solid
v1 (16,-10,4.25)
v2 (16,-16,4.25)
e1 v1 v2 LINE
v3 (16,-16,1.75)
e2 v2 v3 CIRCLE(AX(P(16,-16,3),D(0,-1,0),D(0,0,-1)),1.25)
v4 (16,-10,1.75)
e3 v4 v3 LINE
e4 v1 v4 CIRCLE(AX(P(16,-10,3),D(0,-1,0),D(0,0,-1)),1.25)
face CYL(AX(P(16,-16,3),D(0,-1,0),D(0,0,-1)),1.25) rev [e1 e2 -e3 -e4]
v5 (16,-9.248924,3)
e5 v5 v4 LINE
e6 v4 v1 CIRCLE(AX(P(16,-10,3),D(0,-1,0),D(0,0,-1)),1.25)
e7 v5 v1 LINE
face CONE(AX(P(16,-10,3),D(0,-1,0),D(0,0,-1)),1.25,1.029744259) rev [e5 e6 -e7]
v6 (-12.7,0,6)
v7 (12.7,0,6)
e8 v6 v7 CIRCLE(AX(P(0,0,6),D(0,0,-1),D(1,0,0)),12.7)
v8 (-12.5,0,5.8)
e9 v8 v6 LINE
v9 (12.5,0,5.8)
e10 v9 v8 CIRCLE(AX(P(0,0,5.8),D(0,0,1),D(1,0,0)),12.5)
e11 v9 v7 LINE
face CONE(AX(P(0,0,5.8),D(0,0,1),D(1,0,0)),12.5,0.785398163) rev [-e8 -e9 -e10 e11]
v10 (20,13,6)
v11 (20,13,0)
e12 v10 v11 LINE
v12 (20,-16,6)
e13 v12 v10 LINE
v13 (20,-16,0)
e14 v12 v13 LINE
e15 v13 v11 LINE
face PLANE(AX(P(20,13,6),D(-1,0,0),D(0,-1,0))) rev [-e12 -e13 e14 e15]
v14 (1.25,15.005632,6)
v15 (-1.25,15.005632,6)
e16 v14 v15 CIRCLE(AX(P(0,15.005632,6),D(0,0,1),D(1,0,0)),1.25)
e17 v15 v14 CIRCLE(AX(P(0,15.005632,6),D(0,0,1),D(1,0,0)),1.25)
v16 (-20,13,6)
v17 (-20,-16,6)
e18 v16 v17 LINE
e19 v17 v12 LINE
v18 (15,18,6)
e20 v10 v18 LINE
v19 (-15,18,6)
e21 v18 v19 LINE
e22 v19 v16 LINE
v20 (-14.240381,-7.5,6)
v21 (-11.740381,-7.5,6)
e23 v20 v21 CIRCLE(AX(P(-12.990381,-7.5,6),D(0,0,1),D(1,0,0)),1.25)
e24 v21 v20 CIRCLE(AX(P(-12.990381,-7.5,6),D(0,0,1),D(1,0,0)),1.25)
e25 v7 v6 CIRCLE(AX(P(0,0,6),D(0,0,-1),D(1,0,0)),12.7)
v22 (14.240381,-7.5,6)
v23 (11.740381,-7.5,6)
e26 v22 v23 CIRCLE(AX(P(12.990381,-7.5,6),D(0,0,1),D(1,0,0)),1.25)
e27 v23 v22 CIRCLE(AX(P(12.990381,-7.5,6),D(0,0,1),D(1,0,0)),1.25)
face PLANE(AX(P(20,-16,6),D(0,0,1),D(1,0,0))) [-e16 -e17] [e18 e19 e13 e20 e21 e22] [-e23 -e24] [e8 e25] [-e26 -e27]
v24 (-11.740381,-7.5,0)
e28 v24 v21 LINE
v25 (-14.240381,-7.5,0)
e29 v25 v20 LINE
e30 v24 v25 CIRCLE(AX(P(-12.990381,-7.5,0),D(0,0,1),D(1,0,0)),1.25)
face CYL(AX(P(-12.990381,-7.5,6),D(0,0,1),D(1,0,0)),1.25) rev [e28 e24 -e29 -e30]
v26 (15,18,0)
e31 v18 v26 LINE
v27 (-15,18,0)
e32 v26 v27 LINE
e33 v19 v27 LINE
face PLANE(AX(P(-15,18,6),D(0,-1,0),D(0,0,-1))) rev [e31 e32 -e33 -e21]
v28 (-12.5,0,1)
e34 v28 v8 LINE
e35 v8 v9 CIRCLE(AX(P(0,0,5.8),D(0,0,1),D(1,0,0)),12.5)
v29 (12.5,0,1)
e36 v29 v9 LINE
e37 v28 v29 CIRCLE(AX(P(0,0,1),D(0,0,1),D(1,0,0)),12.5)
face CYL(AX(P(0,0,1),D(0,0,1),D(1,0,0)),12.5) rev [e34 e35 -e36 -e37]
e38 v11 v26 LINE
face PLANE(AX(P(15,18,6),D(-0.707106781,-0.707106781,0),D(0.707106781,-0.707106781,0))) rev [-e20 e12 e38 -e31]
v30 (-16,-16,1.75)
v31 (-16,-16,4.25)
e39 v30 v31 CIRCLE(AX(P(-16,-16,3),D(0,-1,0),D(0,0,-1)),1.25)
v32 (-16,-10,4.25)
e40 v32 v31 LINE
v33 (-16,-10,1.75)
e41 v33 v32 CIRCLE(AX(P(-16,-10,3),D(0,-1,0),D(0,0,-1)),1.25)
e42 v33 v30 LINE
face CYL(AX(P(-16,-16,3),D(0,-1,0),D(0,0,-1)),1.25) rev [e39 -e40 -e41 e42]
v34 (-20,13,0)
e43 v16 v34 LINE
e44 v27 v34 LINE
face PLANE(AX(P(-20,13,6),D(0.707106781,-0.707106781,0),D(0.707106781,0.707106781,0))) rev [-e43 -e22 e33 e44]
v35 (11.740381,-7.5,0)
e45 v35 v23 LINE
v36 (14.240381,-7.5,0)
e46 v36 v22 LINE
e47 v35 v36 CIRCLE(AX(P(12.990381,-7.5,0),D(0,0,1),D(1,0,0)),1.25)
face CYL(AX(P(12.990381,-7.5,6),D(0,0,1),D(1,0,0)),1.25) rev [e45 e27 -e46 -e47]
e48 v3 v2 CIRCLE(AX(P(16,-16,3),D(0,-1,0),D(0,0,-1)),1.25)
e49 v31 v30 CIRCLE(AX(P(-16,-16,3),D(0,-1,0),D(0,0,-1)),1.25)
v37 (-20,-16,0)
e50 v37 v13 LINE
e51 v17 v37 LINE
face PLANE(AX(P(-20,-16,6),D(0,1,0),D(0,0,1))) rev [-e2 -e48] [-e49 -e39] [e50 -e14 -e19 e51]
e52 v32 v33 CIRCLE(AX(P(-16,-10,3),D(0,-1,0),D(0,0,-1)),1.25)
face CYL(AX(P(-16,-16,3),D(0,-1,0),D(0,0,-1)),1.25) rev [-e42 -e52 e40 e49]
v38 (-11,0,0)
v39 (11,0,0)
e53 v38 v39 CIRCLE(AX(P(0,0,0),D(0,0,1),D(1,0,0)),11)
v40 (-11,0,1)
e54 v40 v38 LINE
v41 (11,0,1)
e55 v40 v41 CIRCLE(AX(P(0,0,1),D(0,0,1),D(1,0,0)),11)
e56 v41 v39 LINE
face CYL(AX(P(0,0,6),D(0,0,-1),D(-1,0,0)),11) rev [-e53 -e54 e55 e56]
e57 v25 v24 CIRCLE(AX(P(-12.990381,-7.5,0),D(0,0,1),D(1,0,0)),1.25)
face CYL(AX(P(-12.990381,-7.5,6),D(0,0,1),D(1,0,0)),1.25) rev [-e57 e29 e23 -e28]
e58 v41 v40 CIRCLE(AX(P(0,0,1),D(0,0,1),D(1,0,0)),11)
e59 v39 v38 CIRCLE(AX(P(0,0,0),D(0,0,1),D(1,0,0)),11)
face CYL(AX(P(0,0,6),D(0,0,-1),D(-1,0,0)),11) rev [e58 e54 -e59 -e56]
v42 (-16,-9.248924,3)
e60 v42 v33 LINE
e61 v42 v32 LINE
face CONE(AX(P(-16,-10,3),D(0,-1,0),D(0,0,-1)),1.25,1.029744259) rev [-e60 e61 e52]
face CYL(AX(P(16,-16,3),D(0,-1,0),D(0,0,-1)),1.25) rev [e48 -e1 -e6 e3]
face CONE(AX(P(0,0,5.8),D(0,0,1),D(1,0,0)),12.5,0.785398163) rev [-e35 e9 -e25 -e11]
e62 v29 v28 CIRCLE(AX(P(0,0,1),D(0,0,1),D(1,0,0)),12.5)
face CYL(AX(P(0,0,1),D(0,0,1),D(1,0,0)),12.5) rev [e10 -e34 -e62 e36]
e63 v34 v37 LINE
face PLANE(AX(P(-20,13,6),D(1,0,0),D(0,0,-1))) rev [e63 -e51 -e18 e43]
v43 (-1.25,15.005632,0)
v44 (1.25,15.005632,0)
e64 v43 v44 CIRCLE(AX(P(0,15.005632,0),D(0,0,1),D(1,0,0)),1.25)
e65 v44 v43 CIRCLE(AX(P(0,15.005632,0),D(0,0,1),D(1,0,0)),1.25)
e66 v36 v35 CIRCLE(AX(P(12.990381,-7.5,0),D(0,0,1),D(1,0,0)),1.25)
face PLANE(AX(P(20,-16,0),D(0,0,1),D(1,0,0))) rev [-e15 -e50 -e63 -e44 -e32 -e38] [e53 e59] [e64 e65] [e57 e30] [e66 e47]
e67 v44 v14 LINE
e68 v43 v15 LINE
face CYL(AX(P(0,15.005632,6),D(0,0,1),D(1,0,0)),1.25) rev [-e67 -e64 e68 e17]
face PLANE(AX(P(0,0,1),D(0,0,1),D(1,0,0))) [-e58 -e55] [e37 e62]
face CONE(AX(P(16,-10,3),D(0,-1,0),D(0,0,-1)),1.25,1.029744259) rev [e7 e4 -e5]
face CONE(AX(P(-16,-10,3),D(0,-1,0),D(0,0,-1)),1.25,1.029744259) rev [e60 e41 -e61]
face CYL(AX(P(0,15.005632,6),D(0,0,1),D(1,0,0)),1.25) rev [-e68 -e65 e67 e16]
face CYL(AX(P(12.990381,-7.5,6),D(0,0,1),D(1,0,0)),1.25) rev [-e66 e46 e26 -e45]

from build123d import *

# Parameters (mm, degrees)
SKETCH_1_R             = 11
EXTRUDE_1_DEPTH        = 6
SKETCH_2_R             = 12.5
CUT_EXTRUDE_1_DEPTH    = 5
HOLE_WIZARD_M3_1_D     = 2.5
HOLE_WIZARD_M3_2_D     = 2.5
HOLE_WIZARD_M3_2_DEPTH = 6
HOLE_WIZARD_M3_2_TIP   = 0.751075774
CHAMFER_1_SIZE         = 0.2


with BuildPart() as part:
    # 草图1 → 凸台-拉伸1 (new body)
    with BuildSketch(Plane.XY):
        Polygon((-20, -16), (20, -16), (20, 13), (15, 18), (-15, 18), (-20, 13), align=None)
        Circle(SKETCH_1_R, mode=Mode.SUBTRACT)
    extrude(amount=EXTRUDE_1_DEPTH)

    # 草图2 → 切除-拉伸1 (cut)
    with BuildSketch(Plane.XY.offset(6)):
        Circle(SKETCH_2_R)
    extrude(amount=-CUT_EXTRUDE_1_DEPTH, mode=Mode.SUBTRACT)

    # M3 螺纹孔1 (through all)
    with Locations(Plane(origin=(0, 15.005632156, 6), x_dir=(1, 0, 0), z_dir=(0, 0, 1))):
        with Locations((0, 0), (-12.990381057, -22.505632156), (12.990381057, -22.505632156)):
            Hole(HOLE_WIZARD_M3_1_D / 2)

    # M3 螺纹孔2
    with Locations(Plane(origin=(-16, -16, 3), x_dir=(0, 0, -1), z_dir=(0, -1, 0))):
        with Locations((0, 0), (0, 32)):
            Hole(HOLE_WIZARD_M3_2_D / 2, depth=HOLE_WIZARD_M3_2_DEPTH)
            with Locations((0, 0, -(HOLE_WIZARD_M3_2_DEPTH + HOLE_WIZARD_M3_2_TIP / 2))):  # 118° drill point
                Cone(0, HOLE_WIZARD_M3_2_D / 2, HOLE_WIZARD_M3_2_TIP, mode=Mode.SUBTRACT)

    # 倒角1
    chamfer_1_edges = [part.edges().sort_by_distance(p)[0] for p in [
        (-12.5, 0, 6),
    ]]
    chamfer(chamfer_1_edges, length=CHAMFER_1_SIZE)


solid = part.part
